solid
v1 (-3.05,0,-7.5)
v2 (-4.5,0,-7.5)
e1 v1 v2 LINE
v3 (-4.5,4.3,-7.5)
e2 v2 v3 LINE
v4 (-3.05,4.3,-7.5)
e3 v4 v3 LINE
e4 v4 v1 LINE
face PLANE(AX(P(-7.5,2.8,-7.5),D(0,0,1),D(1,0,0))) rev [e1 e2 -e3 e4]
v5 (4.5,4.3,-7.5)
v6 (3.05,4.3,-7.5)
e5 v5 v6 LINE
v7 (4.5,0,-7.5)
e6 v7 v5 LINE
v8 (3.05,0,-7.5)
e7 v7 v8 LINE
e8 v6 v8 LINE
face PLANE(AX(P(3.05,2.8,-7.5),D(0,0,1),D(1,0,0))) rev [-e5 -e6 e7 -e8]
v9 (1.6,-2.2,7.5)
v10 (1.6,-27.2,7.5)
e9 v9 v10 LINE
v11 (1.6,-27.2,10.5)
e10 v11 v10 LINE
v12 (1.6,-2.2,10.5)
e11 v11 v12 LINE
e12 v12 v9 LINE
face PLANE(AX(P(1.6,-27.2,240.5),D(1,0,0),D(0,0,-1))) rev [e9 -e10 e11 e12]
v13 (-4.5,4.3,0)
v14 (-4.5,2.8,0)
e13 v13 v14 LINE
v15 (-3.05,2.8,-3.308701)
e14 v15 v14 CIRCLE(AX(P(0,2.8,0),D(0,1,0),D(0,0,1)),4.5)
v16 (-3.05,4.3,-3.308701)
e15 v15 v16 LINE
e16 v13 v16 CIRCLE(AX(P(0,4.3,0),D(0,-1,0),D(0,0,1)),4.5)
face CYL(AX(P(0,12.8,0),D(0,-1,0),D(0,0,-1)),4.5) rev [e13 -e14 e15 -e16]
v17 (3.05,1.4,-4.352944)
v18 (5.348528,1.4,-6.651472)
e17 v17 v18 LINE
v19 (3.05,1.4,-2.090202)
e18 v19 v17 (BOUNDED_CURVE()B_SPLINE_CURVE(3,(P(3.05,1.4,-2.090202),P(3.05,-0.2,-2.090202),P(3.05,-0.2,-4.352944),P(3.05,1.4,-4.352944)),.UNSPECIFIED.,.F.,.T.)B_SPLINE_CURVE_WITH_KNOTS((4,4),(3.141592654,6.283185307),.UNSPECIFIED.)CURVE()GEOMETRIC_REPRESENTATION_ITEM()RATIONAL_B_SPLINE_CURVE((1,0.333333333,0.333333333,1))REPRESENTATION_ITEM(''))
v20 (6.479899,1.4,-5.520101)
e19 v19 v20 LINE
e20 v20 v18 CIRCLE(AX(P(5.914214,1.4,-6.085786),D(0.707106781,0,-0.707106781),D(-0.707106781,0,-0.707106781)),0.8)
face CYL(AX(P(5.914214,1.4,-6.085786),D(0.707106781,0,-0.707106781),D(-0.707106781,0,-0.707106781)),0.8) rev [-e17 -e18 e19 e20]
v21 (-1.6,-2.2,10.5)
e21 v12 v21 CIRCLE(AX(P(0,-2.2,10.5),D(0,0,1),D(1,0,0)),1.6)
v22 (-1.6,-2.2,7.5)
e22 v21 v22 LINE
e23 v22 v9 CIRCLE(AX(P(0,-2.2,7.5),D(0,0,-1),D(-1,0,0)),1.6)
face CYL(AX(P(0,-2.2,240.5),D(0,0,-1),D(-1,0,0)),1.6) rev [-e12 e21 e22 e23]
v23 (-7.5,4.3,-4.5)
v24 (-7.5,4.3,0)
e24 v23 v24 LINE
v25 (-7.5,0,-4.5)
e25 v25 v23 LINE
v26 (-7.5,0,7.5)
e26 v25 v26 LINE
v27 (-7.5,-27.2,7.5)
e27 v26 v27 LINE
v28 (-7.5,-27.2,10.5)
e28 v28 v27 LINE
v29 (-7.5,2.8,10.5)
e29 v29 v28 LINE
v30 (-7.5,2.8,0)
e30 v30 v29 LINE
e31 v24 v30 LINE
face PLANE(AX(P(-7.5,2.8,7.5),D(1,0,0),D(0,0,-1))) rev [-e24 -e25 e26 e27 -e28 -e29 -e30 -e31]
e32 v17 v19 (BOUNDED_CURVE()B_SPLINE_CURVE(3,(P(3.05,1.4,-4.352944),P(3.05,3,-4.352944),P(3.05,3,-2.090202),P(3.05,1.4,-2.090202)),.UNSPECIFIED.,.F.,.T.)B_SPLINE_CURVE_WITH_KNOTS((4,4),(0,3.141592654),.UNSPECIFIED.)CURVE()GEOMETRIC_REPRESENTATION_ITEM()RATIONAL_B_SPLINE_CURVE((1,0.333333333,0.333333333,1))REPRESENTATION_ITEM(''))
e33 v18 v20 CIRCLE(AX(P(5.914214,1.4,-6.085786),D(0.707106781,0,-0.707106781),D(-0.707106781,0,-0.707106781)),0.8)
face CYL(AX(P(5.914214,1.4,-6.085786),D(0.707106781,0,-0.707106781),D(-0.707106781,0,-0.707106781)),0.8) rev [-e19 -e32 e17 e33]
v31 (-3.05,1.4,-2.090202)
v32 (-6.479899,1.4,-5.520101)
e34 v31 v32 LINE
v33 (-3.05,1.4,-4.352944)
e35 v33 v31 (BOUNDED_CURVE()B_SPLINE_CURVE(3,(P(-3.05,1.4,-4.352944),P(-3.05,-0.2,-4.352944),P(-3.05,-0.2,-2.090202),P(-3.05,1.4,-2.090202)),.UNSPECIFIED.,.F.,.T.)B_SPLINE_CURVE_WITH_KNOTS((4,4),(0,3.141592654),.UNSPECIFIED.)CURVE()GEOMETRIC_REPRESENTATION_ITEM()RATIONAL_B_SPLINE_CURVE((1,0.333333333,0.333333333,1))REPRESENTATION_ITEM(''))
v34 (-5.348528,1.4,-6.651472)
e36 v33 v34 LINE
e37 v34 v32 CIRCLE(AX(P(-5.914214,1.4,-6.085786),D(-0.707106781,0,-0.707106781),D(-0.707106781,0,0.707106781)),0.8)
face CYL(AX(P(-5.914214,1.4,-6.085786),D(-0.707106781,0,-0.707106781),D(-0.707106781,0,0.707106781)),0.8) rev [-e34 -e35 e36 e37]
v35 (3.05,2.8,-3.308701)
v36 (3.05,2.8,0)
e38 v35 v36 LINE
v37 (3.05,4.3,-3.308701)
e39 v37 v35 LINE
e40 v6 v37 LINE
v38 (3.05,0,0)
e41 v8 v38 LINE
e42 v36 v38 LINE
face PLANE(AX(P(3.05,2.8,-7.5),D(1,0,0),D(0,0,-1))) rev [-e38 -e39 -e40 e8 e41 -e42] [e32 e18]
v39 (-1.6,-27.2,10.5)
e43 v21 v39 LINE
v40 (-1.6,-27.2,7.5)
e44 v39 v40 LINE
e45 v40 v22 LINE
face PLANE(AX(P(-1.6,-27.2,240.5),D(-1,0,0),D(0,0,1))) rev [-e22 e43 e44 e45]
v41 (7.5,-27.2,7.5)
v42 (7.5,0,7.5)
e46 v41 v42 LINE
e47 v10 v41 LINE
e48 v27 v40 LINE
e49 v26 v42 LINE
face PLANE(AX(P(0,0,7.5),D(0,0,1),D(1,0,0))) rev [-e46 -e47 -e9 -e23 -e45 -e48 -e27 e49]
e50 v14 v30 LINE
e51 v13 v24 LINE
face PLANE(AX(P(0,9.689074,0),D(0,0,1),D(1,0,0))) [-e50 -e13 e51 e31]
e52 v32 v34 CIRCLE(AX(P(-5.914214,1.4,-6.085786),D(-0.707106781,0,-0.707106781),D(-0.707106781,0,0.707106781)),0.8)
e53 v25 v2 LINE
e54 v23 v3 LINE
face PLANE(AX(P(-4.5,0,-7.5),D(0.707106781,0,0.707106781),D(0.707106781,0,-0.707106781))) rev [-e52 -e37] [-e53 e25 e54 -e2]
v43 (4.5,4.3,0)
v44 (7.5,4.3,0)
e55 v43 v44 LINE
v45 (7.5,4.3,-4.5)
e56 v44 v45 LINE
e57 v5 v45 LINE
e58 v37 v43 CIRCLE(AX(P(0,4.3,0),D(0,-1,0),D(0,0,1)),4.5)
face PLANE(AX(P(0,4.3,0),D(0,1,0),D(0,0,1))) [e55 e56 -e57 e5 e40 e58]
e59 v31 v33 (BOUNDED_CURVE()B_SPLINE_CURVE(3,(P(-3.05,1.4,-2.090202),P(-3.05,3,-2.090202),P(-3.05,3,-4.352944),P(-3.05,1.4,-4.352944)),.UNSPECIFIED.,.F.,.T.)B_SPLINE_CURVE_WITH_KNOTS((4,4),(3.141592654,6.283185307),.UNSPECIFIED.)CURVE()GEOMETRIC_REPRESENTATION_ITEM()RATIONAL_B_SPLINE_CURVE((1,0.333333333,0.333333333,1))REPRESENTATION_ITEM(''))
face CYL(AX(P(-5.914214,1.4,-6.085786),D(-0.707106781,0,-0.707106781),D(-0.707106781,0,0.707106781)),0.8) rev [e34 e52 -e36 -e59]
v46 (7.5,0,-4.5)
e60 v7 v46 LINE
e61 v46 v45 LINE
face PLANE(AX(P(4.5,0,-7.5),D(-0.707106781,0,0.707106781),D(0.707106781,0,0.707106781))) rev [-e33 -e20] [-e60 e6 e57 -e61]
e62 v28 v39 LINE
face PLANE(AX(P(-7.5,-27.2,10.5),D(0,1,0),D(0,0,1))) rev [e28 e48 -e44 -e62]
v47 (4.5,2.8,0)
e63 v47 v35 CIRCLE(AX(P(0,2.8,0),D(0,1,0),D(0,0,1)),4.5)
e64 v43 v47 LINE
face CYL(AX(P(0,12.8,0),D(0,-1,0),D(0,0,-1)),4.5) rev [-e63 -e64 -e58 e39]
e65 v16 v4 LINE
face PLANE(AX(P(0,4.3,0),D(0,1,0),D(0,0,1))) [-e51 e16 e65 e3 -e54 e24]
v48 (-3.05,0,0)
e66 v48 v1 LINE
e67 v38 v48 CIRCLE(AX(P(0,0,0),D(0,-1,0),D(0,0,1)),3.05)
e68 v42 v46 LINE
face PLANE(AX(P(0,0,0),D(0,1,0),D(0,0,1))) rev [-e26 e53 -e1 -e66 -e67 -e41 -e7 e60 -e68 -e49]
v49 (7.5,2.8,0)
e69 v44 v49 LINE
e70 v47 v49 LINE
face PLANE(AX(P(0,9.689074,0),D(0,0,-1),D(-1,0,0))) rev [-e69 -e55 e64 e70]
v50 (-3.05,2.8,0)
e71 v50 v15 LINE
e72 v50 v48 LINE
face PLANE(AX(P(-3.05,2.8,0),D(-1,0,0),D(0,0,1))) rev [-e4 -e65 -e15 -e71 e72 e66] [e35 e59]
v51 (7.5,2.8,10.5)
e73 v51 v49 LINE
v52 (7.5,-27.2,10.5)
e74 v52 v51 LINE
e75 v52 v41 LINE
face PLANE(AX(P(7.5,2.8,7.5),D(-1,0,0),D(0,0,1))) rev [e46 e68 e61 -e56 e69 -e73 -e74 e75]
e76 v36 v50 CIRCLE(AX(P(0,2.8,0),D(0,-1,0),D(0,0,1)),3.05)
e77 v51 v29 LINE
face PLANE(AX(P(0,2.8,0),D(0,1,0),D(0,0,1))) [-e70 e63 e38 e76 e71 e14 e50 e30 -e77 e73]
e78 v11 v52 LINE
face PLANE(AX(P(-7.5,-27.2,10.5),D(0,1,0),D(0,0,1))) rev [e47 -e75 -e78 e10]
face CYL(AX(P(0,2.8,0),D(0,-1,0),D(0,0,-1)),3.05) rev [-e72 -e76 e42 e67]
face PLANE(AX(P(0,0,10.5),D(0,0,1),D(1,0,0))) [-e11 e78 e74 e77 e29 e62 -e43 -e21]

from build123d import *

# Parameters (mm, degrees)
BOSS_EXTRUDE1_DEPTH = 2.8
SKETCH3_W           = 4.45
SKETCH3_H           = 4.3
BOSS_EXTRUDE2_DEPTH = 1.5
SKETCH4_R           = 4.5
CUT_EXTRUDE2_DEPTH  = 10
BOSS_EXTRUDE3_DEPTH = 1.5
CUT_EXTRUDE5_DEPTH  = 12.445086282
SKETCH17_W          = 15
SKETCH17_H          = 30
BOSS_EXTRUDE4_DEPTH = 3
CUT_EXTRUDE6_DEPTH  = 233


with BuildPart() as part:
    # Sketch1 → Boss-Extrude1 (new body)
    with BuildSketch(Plane(origin=(0, 0, 0), x_dir=(1, 0, 0), z_dir=(0, 1, 0))):
        with BuildLine():
            Line((-3.05, 0), (-3.05, 7.5))
            Line((-3.05, 7.5), (-7.5, 7.5))
            Line((-7.5, 7.5), (-7.5, -7.5))
            Line((-7.5, -7.5), (7.5, -7.5))
            Line((7.5, -7.5), (7.5, 7.5))
            Line((7.5, 7.5), (3.05, 7.5))
            Line((3.05, 7.5), (3.05, 0))
            ThreePointArc((3.05, 0), (0, -3.05), (-3.05, 0))
        make_face()
    extrude(amount=BOSS_EXTRUDE1_DEPTH)

    # Sketch3 → Boss-Extrude2 (add)
    with BuildSketch(Plane(origin=(0, 2.8, 0), x_dir=(1, 0, 0), z_dir=(0, 1, 0))):
        with Locations((-5.275, 5.35)):
            Rectangle(SKETCH3_W, SKETCH3_H)
        with Locations((5.275, 5.35)):
            Rectangle(SKETCH3_W, SKETCH3_H)
    extrude(amount=BOSS_EXTRUDE2_DEPTH)

    # Sketch4 → Cut-Extrude2 (cut)
    with BuildSketch(Plane(origin=(0, 2.8, 0), x_dir=(1, 0, 0), z_dir=(0, 1, 0))):
        Circle(SKETCH4_R)
    extrude(amount=CUT_EXTRUDE2_DEPTH, mode=Mode.SUBTRACT)

    # Sketch5 → Boss-Extrude3 (add)
    with BuildSketch(Plane(origin=(0, 2.8, 0), x_dir=(1, 0, 0), z_dir=(0, 1, 0))):
        with BuildLine():
            Line((-7.5, 3.2), (-7.5, 0))
            Line((-7.5, 0), (-4.5, 0))
            ThreePointArc((-4.5, 0), (-4.152551193, 1.733873868), (-3.163858404, 3.2))
            Line((-3.163858404, 3.2), (-7.5, 3.2))
        make_face()
        with BuildLine():
            ThreePointArc((3.163858404, 3.2), (4.152551193, 1.733873868), (4.5, 0))
            Line((4.5, 0), (7.5, 0))
            Line((7.5, 0), (7.5, 3.2))
            Line((7.5, 3.2), (3.163858404, 3.2))
        make_face()
    extrude(amount=BOSS_EXTRUDE3_DEPTH)

    # Sketch14 → Cut-Extrude5 (cut, through all)
    with BuildSketch(Plane(origin=(0, 4.3, 0), x_dir=(1, 0, 0), z_dir=(0, 1, 0))):
        Polygon((4.5, 7.5), (7.5, 4.5), (7.5, 7.5), align=None)
        Polygon((-7.5, 7.5), (-4.5, 7.5), (-7.5, 4.5), align=None)
    extrude(amount=-CUT_EXTRUDE5_DEPTH, mode=Mode.SUBTRACT)

    # Sketch16 → M2 Tapped Hole1 (revolve, cut)
    with BuildSketch(Plane(origin=(5.914213562, 1.4, -6.085786438), x_dir=(-0.7071067811865475, 0, -0.7071067811865477), z_dir=(0, 1, 0))):
        Polygon((0, 0), (0, 8.480688495), (0.8, 8), (0.8, 0), align=None)
    m2_tapped_hole1 = revolve(axis=Axis((10.404341623, 1.4, -10.575914498), (-0.7071067811865477, 0, 0.7071067811865475)), mode=Mode.SUBTRACT)

    # Mirror1: M2 Tapped Hole1 across plane
    add(m2_tapped_hole1.mirror(Plane(origin=(0, 0, 0), x_dir=(0, 0, 1), z_dir=(1, 0, 0))), mode=Mode.SUBTRACT)

    # Sketch17 → Boss-Extrude4 (add)
    with BuildSketch(Plane.XY.offset(7.5)):
        with Locations((0, -12.2)):
            Rectangle(SKETCH17_W, SKETCH17_H)
    extrude(amount=BOSS_EXTRUDE4_DEPTH)

    # Sketch18 → Cut-Extrude6 (cut)
    with BuildSketch(Plane(origin=(0, 0, 7.5), x_dir=(-1, 0, 0), z_dir=(0, 0, -1))):
        with BuildLine():
            Line((-1.6, -27.2), (-1.6, -2.2))
            ThreePointArc((-1.6, -2.2), (0, -0.6), (1.6, -2.2))
            Line((1.6, -2.2), (1.6, -27.2))
            ThreePointArc((1.6, -27.2), (0, -28.8), (-1.6, -27.2))
        make_face()
    extrude(amount=-CUT_EXTRUDE6_DEPTH, mode=Mode.SUBTRACT)


solid = part.part
